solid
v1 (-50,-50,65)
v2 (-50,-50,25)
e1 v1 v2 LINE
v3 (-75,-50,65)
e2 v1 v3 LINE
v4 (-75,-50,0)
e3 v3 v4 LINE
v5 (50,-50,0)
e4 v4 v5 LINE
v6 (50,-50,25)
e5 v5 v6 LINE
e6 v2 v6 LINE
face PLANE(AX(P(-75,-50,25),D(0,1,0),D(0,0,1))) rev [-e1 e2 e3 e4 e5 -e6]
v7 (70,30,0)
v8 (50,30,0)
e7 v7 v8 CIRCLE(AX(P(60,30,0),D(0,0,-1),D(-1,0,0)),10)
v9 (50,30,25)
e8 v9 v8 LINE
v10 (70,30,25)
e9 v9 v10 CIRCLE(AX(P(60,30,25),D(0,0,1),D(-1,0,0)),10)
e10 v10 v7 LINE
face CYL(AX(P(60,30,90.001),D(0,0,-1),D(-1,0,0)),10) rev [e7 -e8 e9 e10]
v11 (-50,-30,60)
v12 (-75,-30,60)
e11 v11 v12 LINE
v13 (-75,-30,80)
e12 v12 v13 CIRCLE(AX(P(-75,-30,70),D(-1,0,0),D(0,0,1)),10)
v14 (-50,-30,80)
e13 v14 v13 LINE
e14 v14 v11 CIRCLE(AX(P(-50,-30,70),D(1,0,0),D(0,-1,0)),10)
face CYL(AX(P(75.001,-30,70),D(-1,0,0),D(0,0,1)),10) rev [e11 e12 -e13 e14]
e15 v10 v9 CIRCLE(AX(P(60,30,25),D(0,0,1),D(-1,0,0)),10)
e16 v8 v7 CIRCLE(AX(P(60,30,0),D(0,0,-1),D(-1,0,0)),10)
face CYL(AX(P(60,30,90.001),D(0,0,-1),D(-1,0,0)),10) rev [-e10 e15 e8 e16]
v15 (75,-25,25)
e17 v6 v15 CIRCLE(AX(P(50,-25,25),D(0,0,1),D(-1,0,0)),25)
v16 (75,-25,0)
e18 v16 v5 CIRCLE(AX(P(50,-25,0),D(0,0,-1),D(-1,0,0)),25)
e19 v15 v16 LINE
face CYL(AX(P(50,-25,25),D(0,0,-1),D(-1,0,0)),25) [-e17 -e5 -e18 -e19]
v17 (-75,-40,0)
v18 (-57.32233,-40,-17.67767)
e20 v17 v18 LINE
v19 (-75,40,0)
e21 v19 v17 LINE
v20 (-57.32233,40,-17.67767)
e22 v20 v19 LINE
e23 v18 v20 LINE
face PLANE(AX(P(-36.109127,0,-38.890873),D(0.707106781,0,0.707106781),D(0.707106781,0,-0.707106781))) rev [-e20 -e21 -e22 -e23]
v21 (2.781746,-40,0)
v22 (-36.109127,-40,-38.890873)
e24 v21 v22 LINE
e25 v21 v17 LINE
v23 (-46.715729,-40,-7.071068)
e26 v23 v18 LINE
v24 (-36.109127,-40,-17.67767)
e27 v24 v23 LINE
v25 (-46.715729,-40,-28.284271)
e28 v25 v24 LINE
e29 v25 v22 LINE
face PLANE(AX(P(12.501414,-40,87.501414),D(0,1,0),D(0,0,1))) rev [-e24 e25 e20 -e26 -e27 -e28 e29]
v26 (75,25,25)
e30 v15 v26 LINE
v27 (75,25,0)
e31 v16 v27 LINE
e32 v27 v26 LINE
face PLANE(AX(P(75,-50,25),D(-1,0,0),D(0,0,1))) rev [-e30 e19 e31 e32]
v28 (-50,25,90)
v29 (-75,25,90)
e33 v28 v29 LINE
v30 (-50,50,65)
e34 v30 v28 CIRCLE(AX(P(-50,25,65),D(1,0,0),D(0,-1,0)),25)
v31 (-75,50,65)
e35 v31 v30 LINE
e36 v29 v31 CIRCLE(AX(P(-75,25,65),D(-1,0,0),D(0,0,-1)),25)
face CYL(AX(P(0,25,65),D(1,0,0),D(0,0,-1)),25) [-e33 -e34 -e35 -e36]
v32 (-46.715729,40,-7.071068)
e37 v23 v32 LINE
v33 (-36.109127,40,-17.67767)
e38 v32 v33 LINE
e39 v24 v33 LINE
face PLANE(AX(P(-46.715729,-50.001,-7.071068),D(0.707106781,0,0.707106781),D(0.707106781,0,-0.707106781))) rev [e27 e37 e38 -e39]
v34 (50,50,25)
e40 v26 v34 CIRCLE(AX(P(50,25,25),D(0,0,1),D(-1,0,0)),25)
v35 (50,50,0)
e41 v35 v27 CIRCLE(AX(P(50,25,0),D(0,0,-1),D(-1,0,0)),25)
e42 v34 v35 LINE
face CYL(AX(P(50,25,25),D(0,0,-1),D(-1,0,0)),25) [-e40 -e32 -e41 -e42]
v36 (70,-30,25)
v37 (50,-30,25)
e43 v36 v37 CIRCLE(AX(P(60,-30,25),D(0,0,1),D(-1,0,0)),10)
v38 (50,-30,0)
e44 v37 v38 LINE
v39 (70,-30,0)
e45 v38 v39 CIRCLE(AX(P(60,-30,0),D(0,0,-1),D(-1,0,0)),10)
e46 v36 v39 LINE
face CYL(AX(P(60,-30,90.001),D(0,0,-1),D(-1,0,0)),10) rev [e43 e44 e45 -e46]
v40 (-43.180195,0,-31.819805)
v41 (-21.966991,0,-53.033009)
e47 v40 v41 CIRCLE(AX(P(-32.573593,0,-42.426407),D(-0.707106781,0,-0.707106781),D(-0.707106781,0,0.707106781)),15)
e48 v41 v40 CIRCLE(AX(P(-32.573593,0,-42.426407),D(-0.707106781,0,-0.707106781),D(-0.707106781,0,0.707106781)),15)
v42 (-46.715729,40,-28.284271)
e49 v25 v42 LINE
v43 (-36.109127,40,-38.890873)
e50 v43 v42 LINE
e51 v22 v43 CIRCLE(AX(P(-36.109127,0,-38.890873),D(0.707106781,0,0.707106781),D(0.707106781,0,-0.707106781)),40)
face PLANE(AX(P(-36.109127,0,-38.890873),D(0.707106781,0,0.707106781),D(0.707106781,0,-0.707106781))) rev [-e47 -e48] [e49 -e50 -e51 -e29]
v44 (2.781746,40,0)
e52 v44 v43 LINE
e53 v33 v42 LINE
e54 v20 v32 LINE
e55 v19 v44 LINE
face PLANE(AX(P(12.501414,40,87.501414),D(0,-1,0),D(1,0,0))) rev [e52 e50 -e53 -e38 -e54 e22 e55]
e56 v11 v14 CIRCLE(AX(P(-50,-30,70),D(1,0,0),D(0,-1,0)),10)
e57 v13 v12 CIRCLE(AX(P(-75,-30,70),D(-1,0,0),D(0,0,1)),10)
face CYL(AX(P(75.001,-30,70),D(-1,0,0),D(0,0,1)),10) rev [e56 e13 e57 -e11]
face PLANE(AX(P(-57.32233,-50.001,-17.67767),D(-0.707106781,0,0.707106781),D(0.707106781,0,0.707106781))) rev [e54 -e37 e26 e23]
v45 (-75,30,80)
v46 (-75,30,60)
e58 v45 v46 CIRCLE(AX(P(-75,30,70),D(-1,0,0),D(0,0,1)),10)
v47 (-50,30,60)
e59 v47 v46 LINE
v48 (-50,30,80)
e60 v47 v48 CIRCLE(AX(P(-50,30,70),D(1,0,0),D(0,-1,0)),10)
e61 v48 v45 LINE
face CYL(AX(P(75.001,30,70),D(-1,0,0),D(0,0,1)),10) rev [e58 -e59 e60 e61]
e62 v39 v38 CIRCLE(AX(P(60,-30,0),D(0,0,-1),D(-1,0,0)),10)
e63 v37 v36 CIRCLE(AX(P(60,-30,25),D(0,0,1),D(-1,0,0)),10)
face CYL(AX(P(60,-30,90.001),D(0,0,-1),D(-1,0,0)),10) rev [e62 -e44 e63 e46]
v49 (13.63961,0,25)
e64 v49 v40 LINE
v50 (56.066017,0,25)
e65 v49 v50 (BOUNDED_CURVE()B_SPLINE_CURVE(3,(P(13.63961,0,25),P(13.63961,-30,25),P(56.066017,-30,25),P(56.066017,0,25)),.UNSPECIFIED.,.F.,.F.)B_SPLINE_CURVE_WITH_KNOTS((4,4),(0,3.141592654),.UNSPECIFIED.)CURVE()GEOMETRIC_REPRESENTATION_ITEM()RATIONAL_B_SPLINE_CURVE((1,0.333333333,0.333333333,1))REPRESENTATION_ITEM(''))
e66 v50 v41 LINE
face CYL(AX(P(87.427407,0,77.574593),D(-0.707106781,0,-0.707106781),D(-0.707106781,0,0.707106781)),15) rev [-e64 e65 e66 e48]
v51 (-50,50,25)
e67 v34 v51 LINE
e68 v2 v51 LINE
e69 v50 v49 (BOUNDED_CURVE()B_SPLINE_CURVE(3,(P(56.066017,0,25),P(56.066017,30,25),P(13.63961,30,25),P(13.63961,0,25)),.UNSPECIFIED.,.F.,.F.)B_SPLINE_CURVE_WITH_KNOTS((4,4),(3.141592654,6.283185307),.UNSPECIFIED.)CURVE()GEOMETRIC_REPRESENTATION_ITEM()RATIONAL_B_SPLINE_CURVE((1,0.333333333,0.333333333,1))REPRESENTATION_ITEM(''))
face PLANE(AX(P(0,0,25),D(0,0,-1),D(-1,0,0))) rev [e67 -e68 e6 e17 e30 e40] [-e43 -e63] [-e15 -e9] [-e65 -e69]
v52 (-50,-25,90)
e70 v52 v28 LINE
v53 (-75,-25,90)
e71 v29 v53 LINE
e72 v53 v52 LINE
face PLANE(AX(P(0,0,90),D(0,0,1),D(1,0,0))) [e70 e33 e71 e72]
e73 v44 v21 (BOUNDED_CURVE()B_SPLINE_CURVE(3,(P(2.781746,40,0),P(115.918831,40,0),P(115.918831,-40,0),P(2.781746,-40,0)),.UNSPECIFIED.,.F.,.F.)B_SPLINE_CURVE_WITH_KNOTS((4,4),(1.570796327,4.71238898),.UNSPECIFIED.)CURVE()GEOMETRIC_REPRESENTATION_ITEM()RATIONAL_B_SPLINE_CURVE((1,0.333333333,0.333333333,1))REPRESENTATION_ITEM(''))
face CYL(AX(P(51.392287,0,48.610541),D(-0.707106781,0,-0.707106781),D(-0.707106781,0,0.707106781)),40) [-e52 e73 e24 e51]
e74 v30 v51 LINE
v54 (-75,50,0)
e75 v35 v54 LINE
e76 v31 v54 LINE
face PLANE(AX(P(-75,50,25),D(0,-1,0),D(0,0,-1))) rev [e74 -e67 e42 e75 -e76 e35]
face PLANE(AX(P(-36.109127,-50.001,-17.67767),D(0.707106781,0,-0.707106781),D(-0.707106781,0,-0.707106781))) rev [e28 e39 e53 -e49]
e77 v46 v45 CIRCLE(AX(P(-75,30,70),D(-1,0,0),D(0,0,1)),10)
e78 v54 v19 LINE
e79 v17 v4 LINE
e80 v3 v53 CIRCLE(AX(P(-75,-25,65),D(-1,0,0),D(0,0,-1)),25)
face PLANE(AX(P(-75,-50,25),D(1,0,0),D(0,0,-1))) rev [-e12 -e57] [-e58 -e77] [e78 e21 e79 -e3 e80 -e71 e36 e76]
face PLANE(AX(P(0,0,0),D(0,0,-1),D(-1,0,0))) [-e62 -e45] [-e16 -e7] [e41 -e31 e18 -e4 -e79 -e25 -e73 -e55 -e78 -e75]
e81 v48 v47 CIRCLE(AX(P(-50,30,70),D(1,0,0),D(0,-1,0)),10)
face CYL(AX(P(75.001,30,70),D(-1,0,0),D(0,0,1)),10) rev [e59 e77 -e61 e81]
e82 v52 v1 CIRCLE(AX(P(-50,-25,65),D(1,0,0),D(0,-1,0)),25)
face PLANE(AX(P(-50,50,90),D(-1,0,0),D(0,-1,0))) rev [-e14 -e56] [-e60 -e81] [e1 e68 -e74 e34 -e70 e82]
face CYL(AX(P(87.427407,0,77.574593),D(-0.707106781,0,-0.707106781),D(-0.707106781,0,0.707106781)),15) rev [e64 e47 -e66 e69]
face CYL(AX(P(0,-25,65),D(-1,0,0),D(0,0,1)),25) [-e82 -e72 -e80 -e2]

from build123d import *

# Parameters (mm, degrees)
BASE_PLATE_SKETCH_W           = 150
BASE_PLATE_SKETCH_H           = 100
BASE_PLATE_150X100X25_DEPTH   = 25
UPRIGHT_PLATE_SKETCH_W        = 25
UPRIGHT_PLATE_SKETCH_H        = 100
UPRIGHT_PLATE_DEPTH           = 65
ANGLED_BOSS_REACH             = 179.236
BOSS_SLOT_REACH               = 149.733
BOSS_BORE_REACH               = 179.236
BOSS_BORE_SKETCH_R            = 15
BASE_PLATE_HOLES_REACH        = 129.377
BASE_PLATE_HOLES_SKETCH_R     = 10
UPRIGHT_PLATE_HOLES_REACH     = 183.934
UPRIGHT_PLATE_HOLES_SKETCH_R  = 10
UPRIGHT_CORNER_FILLET_R25_A_R = 25
UPRIGHT_CORNER_FILLET_R25_B_R = 25
BASE_CORNER_FILLET_R25_A_R    = 25
BASE_CORNER_FILLET_R25_B_R    = 25


with BuildPart() as part:
    # Base Plate Sketch → Base Plate 150x100x25 (new body)
    with BuildSketch(Plane.XY):
        Rectangle(BASE_PLATE_SKETCH_W, BASE_PLATE_SKETCH_H)
    extrude(amount=BASE_PLATE_150X100X25_DEPTH)

    # Upright Plate Sketch → Upright Plate (add)
    with BuildSketch(Plane.XY.offset(25)):
        with Locations((-62.5, 0)):
            Rectangle(UPRIGHT_PLATE_SKETCH_W, UPRIGHT_PLATE_SKETCH_H)
    extrude(amount=UPRIGHT_PLATE_DEPTH)

    # Angled Boss Sketch → Angled Boss (add, up to next)
    with BuildSketch(Plane(origin=(-37.5, 0, -37.5), x_dir=(0.7071067811865512, 0, -0.7071067811865439), z_dir=(0.7071067811865439, 0, 0.7071067811865512)), mode=Mode.PRIVATE) as angled_boss_sk1:
        with BuildLine():
            Line((-53.033008589, 40), (1.966991411, 40))
            ThreePointArc((1.966991411, 40), (41.966991411, 0), (1.966991411, -40))
            Line((1.966991411, -40), (-53.033008589, -40))
            Line((-53.033008589, -40), (-53.033008589, 40))
        make_face()
    angled_boss_tool1 = extrude(angled_boss_sk1.sketch, amount=ANGLED_BOSS_REACH, mode=Mode.PRIVATE) - part.part
    add(angled_boss_tool1.solids().sort_by_distance((-44.121254, 0, -30.878746))[0])

    # Boss Slot Sketch → Boss Slot (cut, up to next)
    with BuildSketch(Plane(origin=(0, 40, 0), x_dir=(1, 0, 0), z_dir=(0, 1, 0)), mode=Mode.PRIVATE) as boss_slot_sk1:
        Polygon((-57.32233047, 17.67766953), (-46.715728753, 7.071067812), (-36.109127035, 17.67766953), (-46.715728753, 28.284271247), align=None)
    boss_slot_tool1 = extrude(boss_slot_sk1.sketch, amount=-BOSS_SLOT_REACH, mode=Mode.PRIVATE) & part.part
    add(boss_slot_tool1.solids().sort_by_distance((-46.715729, 40, -17.67767))[0], mode=Mode.SUBTRACT)

    # Boss Bore: up to this plane
    boss_bore_end = Plane(origin=(0, 0, 25), z_dir=(0, 0, -1))
    # Boss Bore Sketch → Boss Bore (cut, up to the surface)
    with BuildSketch(Plane(origin=(-37.5, 0, -37.5), x_dir=(-0.7071067811865511, 0, 0.707106781186544), z_dir=(-0.707106781186544, 0, -0.7071067811865511)), mode=Mode.PRIVATE) as boss_bore_sk1:
        with Locations((-6.966991411, 0)):
            Circle(BOSS_BORE_SKETCH_R)
    boss_bore_tool1 = split(extrude(boss_bore_sk1.sketch, amount=-BOSS_BORE_REACH, mode=Mode.PRIVATE), bisect_by=boss_bore_end, keep=Keep.BOTH, mode=Mode.PRIVATE)
    add(boss_bore_tool1.solids().sort_by_distance((-32.573593, 0, -42.426407))[0], mode=Mode.SUBTRACT)

    # Base Plate Holes Sketch → Base Plate Holes (cut, up to next)
    with BuildSketch(Plane(origin=(0, 0, 0), x_dir=(-1, 0, 0), z_dir=(0, 0, -1)), mode=Mode.PRIVATE) as base_plate_holes_sk1:
        with Locations((-60, 30)):
            Circle(BASE_PLATE_HOLES_SKETCH_R)
    base_plate_holes_tool1 = extrude(base_plate_holes_sk1.sketch, amount=-BASE_PLATE_HOLES_REACH, mode=Mode.PRIVATE) & part.part
    # Base Plate Holes Sketch → Base Plate Holes (cut, up to next)
    with BuildSketch(Plane(origin=(0, 0, 0), x_dir=(-1, 0, 0), z_dir=(0, 0, -1)), mode=Mode.PRIVATE) as base_plate_holes_sk2:
        with Locations((-60, -30)):
            Circle(BASE_PLATE_HOLES_SKETCH_R)
    base_plate_holes_tool2 = extrude(base_plate_holes_sk2.sketch, amount=-BASE_PLATE_HOLES_REACH, mode=Mode.PRIVATE) & part.part
    add(base_plate_holes_tool1.solids().sort_by_distance((60, 30, 0))[0], mode=Mode.SUBTRACT)
    add(base_plate_holes_tool2.solids().sort_by_distance((60, -30, 0))[0], mode=Mode.SUBTRACT)

    # Upright Plate Holes Sketch → Upright Plate Holes (cut, up to next)
    with BuildSketch(Plane.ZY.offset(75), mode=Mode.PRIVATE) as upright_plate_holes_sk1:
        with Locations((70, 30)):
            Circle(UPRIGHT_PLATE_HOLES_SKETCH_R)
    upright_plate_holes_tool1 = extrude(upright_plate_holes_sk1.sketch, amount=-UPRIGHT_PLATE_HOLES_REACH, mode=Mode.PRIVATE) & part.part
    # Upright Plate Holes Sketch → Upright Plate Holes (cut, up to next)
    with BuildSketch(Plane.ZY.offset(75), mode=Mode.PRIVATE) as upright_plate_holes_sk2:
        with Locations((70, -30)):
            Circle(UPRIGHT_PLATE_HOLES_SKETCH_R)
    upright_plate_holes_tool2 = extrude(upright_plate_holes_sk2.sketch, amount=-UPRIGHT_PLATE_HOLES_REACH, mode=Mode.PRIVATE) & part.part
    add(upright_plate_holes_tool1.solids().sort_by_distance((-75, 30, 70))[0], mode=Mode.SUBTRACT)
    add(upright_plate_holes_tool2.solids().sort_by_distance((-75, -30, 70))[0], mode=Mode.SUBTRACT)

    # Upright Corner Fillet R25 A
    upright_corner_fillet_r25_a_edges = [part.edges().sort_by_distance(p)[0] for p in [
        (-62.5, 50, 90),
    ]]
    fillet(upright_corner_fillet_r25_a_edges, radius=UPRIGHT_CORNER_FILLET_R25_A_R)

    # Upright Corner Fillet R25 B
    upright_corner_fillet_r25_b_edges = [part.edges().sort_by_distance(p)[0] for p in [
        (-62.5, -50, 90),
    ]]
    fillet(upright_corner_fillet_r25_b_edges, radius=UPRIGHT_CORNER_FILLET_R25_B_R)

    # Base Corner Fillet R25 A
    base_corner_fillet_r25_a_edges = [part.edges().sort_by_distance(p)[0] for p in [
        (75, -50, 12.5),
    ]]
    fillet(base_corner_fillet_r25_a_edges, radius=BASE_CORNER_FILLET_R25_A_R)

    # Base Corner Fillet R25 B
    base_corner_fillet_r25_b_edges = [part.edges().sort_by_distance(p)[0] for p in [
        (75, 50, 12.5),
    ]]
    fillet(base_corner_fillet_r25_b_edges, radius=BASE_CORNER_FILLET_R25_B_R)


solid = part.part
